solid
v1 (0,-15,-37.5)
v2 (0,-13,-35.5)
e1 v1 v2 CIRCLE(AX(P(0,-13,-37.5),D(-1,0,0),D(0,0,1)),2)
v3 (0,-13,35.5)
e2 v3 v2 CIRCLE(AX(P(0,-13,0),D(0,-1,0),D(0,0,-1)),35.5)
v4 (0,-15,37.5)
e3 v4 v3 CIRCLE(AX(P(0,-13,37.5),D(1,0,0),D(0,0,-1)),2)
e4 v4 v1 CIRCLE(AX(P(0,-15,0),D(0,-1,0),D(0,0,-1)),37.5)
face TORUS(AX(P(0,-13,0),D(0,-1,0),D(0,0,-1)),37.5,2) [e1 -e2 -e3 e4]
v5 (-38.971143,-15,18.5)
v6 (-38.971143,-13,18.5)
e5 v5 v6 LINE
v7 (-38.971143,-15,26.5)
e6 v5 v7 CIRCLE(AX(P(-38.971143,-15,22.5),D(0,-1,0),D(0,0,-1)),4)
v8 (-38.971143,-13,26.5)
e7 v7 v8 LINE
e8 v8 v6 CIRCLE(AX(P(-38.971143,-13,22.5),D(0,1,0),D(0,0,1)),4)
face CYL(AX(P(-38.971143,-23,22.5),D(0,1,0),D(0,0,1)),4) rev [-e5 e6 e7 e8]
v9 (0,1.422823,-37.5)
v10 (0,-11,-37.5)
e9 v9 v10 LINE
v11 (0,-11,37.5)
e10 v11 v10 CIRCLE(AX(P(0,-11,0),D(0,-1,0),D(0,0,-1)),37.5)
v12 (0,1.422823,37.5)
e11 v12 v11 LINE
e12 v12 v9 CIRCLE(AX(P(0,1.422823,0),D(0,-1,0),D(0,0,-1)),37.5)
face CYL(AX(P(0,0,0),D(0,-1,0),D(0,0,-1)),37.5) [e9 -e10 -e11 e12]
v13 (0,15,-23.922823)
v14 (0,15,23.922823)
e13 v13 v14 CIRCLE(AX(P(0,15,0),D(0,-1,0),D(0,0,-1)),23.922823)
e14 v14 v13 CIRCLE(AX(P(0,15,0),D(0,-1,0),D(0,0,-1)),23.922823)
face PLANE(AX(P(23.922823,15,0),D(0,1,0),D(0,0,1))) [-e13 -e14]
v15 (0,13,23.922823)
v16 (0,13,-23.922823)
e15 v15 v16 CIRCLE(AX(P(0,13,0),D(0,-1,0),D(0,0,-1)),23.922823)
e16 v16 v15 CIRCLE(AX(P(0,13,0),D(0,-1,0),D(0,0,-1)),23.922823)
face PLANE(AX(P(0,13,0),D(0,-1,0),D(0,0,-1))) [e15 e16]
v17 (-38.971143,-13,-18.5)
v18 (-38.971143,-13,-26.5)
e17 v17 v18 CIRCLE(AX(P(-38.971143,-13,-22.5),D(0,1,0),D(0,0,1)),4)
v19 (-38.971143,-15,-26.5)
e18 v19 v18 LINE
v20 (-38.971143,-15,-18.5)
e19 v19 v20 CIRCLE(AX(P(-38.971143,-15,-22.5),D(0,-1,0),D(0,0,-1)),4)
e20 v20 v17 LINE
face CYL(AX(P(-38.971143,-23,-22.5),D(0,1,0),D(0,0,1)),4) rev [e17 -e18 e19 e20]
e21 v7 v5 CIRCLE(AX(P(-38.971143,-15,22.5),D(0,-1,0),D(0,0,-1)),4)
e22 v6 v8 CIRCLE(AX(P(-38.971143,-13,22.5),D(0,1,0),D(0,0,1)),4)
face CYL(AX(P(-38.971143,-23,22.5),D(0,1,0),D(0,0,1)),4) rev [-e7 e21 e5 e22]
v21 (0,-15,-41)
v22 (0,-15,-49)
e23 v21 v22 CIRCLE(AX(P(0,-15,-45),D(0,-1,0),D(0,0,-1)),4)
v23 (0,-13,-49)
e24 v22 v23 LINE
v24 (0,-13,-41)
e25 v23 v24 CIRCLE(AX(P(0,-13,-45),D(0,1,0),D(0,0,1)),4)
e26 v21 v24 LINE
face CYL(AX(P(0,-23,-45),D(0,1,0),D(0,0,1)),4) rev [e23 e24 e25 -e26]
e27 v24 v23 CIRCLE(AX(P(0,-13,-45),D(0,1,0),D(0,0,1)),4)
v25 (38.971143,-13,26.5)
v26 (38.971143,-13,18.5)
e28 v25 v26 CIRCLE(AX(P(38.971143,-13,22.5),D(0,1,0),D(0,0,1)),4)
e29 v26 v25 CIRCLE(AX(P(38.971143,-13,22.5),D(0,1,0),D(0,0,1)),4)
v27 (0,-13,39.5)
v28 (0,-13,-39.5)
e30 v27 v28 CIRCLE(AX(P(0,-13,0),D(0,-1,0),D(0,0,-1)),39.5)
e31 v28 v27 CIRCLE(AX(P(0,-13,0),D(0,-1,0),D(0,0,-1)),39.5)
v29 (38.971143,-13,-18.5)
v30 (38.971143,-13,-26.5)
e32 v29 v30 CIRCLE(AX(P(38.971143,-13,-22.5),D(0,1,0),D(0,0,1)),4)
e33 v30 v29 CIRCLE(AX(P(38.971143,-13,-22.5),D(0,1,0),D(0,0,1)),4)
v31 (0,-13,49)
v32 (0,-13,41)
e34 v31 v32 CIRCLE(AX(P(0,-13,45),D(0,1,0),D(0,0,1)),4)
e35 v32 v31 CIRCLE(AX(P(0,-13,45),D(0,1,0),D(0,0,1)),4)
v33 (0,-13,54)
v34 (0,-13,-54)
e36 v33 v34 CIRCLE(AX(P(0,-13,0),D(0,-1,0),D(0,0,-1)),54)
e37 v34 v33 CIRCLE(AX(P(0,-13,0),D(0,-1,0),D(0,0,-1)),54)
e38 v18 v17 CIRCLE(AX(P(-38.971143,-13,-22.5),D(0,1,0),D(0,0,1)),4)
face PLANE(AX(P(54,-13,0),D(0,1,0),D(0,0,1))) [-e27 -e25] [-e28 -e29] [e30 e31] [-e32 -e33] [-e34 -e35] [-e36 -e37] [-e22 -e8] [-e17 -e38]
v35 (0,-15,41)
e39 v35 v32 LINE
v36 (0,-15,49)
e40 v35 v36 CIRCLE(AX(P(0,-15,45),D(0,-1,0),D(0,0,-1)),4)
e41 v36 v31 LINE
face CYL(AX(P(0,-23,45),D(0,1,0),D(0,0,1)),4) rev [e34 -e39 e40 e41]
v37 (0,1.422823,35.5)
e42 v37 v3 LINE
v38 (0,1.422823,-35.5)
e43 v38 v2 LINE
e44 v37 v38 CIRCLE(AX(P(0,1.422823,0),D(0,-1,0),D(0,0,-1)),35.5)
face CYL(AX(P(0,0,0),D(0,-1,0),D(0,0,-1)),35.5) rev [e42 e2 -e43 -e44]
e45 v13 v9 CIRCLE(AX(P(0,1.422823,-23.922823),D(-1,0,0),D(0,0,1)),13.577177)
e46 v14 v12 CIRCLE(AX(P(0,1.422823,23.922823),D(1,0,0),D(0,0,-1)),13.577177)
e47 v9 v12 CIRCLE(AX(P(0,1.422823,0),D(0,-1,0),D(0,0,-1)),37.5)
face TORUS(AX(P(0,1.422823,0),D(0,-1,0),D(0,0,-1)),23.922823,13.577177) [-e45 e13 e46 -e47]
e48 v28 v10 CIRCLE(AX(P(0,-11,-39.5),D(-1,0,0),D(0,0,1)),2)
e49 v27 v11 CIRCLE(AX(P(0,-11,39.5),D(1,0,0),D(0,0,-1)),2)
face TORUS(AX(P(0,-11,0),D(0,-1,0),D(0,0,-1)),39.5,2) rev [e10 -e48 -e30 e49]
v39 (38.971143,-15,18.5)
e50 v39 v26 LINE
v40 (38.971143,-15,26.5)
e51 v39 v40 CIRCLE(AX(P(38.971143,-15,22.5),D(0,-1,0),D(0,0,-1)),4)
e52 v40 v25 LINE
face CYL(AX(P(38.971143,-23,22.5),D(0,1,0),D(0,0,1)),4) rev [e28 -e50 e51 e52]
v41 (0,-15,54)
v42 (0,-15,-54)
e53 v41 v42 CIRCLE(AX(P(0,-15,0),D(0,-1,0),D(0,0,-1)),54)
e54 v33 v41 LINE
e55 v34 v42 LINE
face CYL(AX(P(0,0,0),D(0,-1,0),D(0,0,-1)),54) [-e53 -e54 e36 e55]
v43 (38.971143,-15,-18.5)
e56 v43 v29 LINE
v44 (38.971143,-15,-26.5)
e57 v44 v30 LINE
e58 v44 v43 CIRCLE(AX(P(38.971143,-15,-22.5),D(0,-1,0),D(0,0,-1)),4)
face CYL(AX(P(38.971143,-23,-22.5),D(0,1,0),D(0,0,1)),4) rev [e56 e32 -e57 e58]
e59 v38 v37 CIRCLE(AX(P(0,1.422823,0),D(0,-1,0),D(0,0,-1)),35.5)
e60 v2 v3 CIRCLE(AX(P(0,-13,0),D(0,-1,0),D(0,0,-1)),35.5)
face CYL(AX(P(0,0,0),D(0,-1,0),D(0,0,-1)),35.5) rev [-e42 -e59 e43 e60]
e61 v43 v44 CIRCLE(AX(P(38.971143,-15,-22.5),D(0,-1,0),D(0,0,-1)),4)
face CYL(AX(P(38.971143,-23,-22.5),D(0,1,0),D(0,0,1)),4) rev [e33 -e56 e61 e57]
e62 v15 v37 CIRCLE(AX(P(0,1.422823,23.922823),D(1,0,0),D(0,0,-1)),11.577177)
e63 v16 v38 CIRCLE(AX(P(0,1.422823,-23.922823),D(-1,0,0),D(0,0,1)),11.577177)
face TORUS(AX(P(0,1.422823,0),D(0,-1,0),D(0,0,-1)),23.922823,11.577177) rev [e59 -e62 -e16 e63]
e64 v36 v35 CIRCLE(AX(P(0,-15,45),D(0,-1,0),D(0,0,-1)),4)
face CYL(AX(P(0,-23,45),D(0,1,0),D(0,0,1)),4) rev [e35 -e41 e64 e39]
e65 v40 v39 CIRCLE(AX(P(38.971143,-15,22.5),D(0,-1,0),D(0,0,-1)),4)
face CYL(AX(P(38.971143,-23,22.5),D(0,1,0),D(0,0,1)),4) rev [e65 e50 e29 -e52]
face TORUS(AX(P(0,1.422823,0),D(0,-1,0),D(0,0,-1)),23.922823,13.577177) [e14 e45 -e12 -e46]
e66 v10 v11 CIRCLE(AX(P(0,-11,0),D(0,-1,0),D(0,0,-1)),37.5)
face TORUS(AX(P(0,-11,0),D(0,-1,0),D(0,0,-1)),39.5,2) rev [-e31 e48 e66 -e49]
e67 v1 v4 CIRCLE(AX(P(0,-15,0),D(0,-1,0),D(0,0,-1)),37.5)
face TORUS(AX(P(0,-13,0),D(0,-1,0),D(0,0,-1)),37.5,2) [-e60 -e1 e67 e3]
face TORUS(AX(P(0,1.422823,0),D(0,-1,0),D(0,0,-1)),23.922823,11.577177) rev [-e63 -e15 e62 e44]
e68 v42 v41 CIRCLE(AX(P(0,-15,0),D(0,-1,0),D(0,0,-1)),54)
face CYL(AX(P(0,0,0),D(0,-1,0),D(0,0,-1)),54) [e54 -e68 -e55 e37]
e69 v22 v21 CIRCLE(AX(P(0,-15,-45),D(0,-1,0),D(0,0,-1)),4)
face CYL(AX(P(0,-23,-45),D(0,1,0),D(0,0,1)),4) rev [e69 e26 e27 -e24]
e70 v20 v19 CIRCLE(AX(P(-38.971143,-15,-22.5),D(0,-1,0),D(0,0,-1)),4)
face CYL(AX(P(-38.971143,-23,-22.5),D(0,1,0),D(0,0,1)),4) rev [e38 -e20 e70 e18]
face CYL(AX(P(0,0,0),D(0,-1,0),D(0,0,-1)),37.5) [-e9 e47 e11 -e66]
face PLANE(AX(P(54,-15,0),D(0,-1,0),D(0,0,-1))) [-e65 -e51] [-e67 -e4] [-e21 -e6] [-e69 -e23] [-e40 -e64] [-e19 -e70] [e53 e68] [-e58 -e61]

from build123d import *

# Parameters (mm, degrees)
SKETCH_2_R          = 4
CUT_EXTRUDE_1_DEPTH = 10


with BuildPart() as part:
    # 草图1 → 旋转1 (revolve)
    with BuildSketch(Plane.XY, mode=Mode.PRIVATE) as revolve_1_sk:
        with BuildLine():
            Line((54, -13), (39.5, -13))
            ThreePointArc((39.5, -13), (38.085786438, -12.414213562), (37.5, -11))
            Line((37.5, -11), (37.5, 1.42282291))
            ThreePointArc((37.5, 1.42282291), (33.5233369, 11.0233369), (23.92282291, 15))
            Line((23.92282291, 15), (0, 15))
            Line((0, 15), (0, 13))
            Line((0, 13), (23.92282291, 13))
            ThreePointArc((23.92282291, 13), (32.109123337, 9.609123337), (35.5, 1.42282291))
            Line((35.5, 1.42282291), (35.5, -13))
            ThreePointArc((35.5, -13), (36.085786438, -14.414213562), (37.5, -15))
            Line((37.5, -15), (54, -15))
            Line((54, -15), (54, -13))
        make_face()
    revolve(revolve_1_sk.sketch.rotate(Axis((0, 0, 0), (0, 1, 0)), 90), axis=Axis((0, 0, 0), (0, 1, 0)))

    # 草图2 → 切除-拉伸1 (cut)
    with BuildSketch(Plane(origin=(0, -13, 0), x_dir=(1, 0, 0), z_dir=(0, 1, 0))):
        with Locations(Location((0, 45, 0), (0, 0, 270))):
            Circle(SKETCH_2_R)
        with Locations(Location((38.97114317, 22.5, 0), (0, 0, 270))):
            Circle(SKETCH_2_R)
        with Locations(Location((38.97114317, -22.5, 0), (0, 0, 270))):
            Circle(SKETCH_2_R)
        with Locations(Location((0, -45, 0), (0, 0, 270))):
            Circle(SKETCH_2_R)
        with Locations(Location((-38.97114317, -22.5, 0), (0, 0, 270))):
            Circle(SKETCH_2_R)
        with Locations(Location((-38.97114317, 22.5, 0), (0, 0, 270))):
            Circle(SKETCH_2_R)
    extrude(amount=-CUT_EXTRUDE_1_DEPTH, mode=Mode.SUBTRACT)


solid = part.part
